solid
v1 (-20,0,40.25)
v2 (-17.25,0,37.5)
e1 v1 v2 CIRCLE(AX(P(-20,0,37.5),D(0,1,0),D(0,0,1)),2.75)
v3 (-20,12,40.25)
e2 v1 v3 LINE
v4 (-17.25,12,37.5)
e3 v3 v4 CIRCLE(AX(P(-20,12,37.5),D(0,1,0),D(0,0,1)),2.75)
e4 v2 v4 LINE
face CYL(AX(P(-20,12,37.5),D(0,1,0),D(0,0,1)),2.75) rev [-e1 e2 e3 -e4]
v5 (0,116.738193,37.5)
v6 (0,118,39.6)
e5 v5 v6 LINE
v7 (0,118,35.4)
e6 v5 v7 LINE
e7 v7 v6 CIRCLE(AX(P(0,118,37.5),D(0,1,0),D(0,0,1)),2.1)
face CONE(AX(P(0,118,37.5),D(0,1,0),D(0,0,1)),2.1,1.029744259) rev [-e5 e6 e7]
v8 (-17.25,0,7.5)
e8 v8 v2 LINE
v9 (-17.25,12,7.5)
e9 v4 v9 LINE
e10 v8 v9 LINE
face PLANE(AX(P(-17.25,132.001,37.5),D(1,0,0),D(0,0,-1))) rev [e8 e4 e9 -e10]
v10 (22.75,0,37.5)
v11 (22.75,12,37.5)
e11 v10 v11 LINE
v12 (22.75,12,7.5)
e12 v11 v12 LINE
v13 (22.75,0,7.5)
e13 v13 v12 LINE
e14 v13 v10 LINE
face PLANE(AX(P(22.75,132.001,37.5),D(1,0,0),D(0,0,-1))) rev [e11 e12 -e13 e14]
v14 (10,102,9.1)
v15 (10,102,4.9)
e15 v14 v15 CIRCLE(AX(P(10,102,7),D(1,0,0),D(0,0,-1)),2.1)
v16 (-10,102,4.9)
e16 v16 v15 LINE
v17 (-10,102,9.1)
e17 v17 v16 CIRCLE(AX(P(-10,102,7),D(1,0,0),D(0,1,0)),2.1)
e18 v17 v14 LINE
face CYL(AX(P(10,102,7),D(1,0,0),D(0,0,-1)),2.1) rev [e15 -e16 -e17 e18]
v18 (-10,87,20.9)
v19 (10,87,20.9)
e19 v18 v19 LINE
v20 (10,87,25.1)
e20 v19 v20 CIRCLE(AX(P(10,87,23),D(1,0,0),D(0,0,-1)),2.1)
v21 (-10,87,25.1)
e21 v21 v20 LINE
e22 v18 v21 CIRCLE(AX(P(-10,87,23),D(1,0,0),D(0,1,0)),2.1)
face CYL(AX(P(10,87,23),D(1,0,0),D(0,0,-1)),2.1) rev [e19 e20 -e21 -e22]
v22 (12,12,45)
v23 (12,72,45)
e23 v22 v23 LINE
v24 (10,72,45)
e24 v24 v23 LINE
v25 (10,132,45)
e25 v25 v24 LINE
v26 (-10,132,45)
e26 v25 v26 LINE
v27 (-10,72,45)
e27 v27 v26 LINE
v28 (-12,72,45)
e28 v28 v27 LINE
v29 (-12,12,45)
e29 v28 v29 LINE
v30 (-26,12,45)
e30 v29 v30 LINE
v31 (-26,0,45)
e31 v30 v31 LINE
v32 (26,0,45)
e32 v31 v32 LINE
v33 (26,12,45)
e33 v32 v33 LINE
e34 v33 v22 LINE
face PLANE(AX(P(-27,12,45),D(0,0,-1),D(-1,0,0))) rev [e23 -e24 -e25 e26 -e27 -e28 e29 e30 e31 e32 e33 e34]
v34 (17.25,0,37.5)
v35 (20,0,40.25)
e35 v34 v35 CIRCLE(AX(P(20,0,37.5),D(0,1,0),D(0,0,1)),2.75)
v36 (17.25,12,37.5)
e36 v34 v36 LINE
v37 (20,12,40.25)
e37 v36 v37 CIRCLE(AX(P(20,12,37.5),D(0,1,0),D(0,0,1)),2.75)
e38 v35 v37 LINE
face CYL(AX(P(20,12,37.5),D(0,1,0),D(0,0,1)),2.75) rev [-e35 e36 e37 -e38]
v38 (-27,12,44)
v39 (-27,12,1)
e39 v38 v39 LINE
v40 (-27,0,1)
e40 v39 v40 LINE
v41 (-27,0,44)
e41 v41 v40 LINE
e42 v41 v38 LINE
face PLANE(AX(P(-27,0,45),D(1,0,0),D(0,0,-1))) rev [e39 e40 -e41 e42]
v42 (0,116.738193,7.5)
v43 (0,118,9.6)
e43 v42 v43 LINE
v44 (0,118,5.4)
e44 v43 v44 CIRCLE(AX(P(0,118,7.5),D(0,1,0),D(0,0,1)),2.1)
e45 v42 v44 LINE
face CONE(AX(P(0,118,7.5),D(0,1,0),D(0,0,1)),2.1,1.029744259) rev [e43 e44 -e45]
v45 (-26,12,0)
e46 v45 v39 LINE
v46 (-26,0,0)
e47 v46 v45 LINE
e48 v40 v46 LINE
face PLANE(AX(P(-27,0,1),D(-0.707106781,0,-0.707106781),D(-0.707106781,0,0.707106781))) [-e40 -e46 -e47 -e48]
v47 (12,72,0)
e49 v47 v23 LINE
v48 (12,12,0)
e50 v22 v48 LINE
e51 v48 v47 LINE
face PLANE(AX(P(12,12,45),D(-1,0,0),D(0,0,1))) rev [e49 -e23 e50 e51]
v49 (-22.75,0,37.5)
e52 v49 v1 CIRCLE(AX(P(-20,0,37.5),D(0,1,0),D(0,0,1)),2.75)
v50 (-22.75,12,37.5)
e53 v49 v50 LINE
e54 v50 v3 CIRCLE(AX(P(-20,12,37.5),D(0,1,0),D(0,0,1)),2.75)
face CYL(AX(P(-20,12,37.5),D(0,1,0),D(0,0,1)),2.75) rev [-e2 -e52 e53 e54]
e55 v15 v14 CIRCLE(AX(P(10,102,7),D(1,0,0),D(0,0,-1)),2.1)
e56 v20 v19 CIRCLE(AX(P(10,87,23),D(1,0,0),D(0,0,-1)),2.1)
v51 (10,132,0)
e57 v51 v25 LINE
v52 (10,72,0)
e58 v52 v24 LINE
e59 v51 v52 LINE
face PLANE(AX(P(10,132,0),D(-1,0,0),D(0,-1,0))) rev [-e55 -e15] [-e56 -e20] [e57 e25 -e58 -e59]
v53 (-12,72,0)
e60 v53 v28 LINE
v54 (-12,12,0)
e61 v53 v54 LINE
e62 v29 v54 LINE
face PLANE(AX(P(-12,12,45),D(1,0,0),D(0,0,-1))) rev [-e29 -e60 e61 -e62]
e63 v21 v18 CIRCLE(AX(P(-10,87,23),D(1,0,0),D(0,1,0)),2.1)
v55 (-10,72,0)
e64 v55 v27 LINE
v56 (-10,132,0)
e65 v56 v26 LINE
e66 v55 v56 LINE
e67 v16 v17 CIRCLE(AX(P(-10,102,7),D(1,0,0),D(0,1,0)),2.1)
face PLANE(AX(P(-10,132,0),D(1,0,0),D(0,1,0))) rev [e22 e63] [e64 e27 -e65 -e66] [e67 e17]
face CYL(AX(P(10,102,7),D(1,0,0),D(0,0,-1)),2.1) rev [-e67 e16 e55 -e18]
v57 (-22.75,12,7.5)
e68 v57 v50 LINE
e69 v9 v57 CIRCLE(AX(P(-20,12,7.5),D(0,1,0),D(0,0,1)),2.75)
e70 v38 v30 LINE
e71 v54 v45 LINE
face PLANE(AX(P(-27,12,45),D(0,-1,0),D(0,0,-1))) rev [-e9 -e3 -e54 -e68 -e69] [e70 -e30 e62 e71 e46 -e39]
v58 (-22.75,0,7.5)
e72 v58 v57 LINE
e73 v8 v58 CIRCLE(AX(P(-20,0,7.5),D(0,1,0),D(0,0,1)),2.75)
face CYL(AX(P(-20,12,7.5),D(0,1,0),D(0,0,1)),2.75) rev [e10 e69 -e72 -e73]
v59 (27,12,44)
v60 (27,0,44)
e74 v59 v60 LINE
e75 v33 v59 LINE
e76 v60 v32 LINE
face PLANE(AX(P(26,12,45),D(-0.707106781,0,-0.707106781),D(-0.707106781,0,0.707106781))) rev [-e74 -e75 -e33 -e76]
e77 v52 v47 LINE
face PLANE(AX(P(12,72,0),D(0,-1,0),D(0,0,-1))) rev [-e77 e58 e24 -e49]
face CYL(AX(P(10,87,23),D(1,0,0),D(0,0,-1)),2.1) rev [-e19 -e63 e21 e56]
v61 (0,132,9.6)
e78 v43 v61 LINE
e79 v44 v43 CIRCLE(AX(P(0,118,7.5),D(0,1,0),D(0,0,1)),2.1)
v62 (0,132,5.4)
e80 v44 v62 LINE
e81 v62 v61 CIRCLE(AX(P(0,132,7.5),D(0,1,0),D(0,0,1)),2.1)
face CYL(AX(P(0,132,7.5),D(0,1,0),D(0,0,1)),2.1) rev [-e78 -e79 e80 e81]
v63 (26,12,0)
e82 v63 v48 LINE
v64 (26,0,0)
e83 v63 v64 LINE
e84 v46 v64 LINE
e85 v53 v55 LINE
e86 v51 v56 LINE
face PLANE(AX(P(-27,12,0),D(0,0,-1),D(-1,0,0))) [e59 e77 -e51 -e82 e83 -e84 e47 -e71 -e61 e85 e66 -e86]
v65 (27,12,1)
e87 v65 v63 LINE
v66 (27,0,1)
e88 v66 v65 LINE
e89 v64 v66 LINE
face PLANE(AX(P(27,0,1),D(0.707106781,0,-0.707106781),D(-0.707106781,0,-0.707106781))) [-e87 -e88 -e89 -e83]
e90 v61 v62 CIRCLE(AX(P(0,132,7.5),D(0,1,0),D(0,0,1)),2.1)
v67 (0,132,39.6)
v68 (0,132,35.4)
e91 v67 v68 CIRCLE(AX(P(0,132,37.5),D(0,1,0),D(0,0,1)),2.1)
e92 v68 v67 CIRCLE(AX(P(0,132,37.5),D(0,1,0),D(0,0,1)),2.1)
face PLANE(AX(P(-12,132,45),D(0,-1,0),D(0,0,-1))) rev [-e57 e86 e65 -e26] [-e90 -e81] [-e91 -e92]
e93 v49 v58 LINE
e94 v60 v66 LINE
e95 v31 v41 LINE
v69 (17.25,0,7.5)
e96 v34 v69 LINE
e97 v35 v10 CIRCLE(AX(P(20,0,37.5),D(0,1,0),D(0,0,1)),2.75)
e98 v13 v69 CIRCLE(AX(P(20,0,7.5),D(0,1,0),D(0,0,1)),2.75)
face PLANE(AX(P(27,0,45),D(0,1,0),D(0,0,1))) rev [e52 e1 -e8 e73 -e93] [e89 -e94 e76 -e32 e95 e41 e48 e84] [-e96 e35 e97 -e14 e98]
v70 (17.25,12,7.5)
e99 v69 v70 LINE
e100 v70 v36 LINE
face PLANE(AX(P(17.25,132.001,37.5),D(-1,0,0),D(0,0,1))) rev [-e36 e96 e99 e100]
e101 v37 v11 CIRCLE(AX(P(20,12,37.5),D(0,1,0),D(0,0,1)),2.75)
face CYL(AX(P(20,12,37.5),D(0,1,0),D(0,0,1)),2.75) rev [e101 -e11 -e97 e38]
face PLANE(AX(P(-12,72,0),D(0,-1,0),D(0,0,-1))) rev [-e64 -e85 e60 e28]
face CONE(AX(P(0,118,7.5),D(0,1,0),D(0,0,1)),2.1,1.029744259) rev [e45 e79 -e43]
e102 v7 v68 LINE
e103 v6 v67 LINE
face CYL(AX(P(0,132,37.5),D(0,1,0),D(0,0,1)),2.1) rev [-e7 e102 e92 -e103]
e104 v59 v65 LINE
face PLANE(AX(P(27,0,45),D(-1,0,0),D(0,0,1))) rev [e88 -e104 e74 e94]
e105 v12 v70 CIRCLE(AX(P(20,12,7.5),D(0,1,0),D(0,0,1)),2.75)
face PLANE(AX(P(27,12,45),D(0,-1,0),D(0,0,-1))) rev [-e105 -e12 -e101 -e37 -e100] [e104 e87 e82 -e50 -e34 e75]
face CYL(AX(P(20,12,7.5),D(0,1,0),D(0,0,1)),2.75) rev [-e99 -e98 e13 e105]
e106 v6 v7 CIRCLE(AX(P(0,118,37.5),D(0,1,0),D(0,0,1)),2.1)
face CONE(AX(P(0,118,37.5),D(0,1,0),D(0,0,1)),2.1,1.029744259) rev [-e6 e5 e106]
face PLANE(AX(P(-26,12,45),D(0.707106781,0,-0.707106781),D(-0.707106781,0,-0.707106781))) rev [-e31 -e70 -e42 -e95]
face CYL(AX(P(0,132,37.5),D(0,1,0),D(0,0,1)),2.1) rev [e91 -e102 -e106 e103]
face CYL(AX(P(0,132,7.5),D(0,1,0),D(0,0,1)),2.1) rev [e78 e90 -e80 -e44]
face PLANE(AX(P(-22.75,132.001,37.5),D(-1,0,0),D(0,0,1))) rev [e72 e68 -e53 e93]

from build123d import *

# Parameters (mm, degrees)
BOSS_EXTRUDE1_DEPTH            = 45
SKETCH9_W                      = 2
SKETCH9_H                      = 60
CUT_EXTRUDE1_DEPTH             = 143.049287221
M5_TAPPED_HOLE2_D              = 4.2
F_5_5_5_5_DIAMETER_HOLE1_D     = 5.5
F_5_5_5_5_DIAMETER_HOLE1_DEPTH = 20
F_5_5_5_5_DIAMETER_HOLE1_TIP   = 1.652366702
CHAMFER1_SIZE                  = 1
M5_TAPPED_HOLE3_D              = 4.2
M5_TAPPED_HOLE3_DEPTH          = 14
M5_TAPPED_HOLE3_TIP            = 1.2618073
CUT_EXTRUDE2_REACH             = 144.049


with BuildPart() as part:
    # Sketch1 → Boss-Extrude1 (new body)
    with BuildSketch(Plane.XY):
        Polygon((27, 0), (-27, 0), (-27, 12), (-12, 12), (-12, 132), (12, 132), (12, 12), (27, 12), align=None)
    extrude(amount=BOSS_EXTRUDE1_DEPTH)

    # Sketch9 → Cut-Extrude1 (cut, through all)
    with BuildSketch(Plane.XY.offset(45)):
        with Locations((-11, 102)):
            Rectangle(SKETCH9_W, SKETCH9_H)
        with Locations((11, 102)):
            Rectangle(SKETCH9_W, SKETCH9_H)
    extrude(amount=-CUT_EXTRUDE1_DEPTH, mode=Mode.SUBTRACT)

    # M5 Tapped Hole2 (through all)
    with Locations(Plane(origin=(10, -0.235974088, -1.632115168), x_dir=(0, 0, -1), z_dir=(1, 0, 0))):
        with Locations((-8.632115168, 102.235974088), (-24.632115168, 87.235974088)):
            Hole(M5_TAPPED_HOLE2_D / 2)

    # Ø5.5 (5.5) Diameter Hole1
    with Locations(Plane(origin=(0, 12, 0), x_dir=(-1, 0, 0), z_dir=(0, 1, 0))):
        with Locations((20, 7.5), (20, 37.5), (-20, 37.5), (-20, 7.5)):
            Hole(F_5_5_5_5_DIAMETER_HOLE1_D / 2, depth=F_5_5_5_5_DIAMETER_HOLE1_DEPTH)
            with Locations((0, 0, -(F_5_5_5_5_DIAMETER_HOLE1_DEPTH + F_5_5_5_5_DIAMETER_HOLE1_TIP / 2))):  # 118° drill point
                Cone(0, F_5_5_5_5_DIAMETER_HOLE1_D / 2, F_5_5_5_5_DIAMETER_HOLE1_TIP, mode=Mode.SUBTRACT)

    # Chamfer1
    chamfer1_edges = [part.edges().sort_by_distance(p)[0] for p in [
        (27, 6, 45),
        (-27, 6, 0),
        (-27, 6, 45),
        (27, 6, 0),
    ]]
    chamfer(chamfer1_edges, length=CHAMFER1_SIZE)

    # M5 Tapped Hole3
    with Locations(Plane(origin=(0, 132, 0), x_dir=(-1, 0, 0), z_dir=(0, 1, 0))):
        with Locations((0, 37.5), (0, 7.5)):
            Hole(M5_TAPPED_HOLE3_D / 2, depth=M5_TAPPED_HOLE3_DEPTH)
            with Locations((0, 0, -(M5_TAPPED_HOLE3_DEPTH + M5_TAPPED_HOLE3_TIP / 2))):  # 118° drill point
                Cone(0, M5_TAPPED_HOLE3_D / 2, M5_TAPPED_HOLE3_TIP, mode=Mode.SUBTRACT)

    # Sketch12 → Cut-Extrude2 (cut, up to next)
    with BuildSketch(Plane.XZ, mode=Mode.PRIVATE) as cut_extrude2_sk1:
        with BuildLine():
            Line((-17.25, 37.5), (-17.25, 7.5))
            ThreePointArc((-17.25, 7.5), (-20, 4.75), (-22.75, 7.5))
            Line((-22.75, 7.5), (-22.75, 37.5))
            ThreePointArc((-22.75, 37.5), (-20, 40.25), (-17.25, 37.5))
        make_face()
    cut_extrude2_tool1 = extrude(cut_extrude2_sk1.sketch, amount=-CUT_EXTRUDE2_REACH, mode=Mode.PRIVATE) & part.part
    # Sketch12 → Cut-Extrude2 (cut, up to next)
    with BuildSketch(Plane.XZ, mode=Mode.PRIVATE) as cut_extrude2_sk2:
        with BuildLine():
            Line((22.75, 37.5), (22.75, 7.5))
            ThreePointArc((22.75, 7.5), (20, 4.75), (17.25, 7.5))
            Line((17.25, 7.5), (17.25, 37.5))
            ThreePointArc((17.25, 37.5), (20, 40.25), (22.75, 37.5))
        make_face()
    cut_extrude2_tool2 = extrude(cut_extrude2_sk2.sketch, amount=-CUT_EXTRUDE2_REACH, mode=Mode.PRIVATE) & part.part
    add(cut_extrude2_tool1.solids().sort_by_distance((-20, 0, 22.5))[0], mode=Mode.SUBTRACT)
    add(cut_extrude2_tool2.solids().sort_by_distance((20, 0, 22.5))[0], mode=Mode.SUBTRACT)


solid = part.part
